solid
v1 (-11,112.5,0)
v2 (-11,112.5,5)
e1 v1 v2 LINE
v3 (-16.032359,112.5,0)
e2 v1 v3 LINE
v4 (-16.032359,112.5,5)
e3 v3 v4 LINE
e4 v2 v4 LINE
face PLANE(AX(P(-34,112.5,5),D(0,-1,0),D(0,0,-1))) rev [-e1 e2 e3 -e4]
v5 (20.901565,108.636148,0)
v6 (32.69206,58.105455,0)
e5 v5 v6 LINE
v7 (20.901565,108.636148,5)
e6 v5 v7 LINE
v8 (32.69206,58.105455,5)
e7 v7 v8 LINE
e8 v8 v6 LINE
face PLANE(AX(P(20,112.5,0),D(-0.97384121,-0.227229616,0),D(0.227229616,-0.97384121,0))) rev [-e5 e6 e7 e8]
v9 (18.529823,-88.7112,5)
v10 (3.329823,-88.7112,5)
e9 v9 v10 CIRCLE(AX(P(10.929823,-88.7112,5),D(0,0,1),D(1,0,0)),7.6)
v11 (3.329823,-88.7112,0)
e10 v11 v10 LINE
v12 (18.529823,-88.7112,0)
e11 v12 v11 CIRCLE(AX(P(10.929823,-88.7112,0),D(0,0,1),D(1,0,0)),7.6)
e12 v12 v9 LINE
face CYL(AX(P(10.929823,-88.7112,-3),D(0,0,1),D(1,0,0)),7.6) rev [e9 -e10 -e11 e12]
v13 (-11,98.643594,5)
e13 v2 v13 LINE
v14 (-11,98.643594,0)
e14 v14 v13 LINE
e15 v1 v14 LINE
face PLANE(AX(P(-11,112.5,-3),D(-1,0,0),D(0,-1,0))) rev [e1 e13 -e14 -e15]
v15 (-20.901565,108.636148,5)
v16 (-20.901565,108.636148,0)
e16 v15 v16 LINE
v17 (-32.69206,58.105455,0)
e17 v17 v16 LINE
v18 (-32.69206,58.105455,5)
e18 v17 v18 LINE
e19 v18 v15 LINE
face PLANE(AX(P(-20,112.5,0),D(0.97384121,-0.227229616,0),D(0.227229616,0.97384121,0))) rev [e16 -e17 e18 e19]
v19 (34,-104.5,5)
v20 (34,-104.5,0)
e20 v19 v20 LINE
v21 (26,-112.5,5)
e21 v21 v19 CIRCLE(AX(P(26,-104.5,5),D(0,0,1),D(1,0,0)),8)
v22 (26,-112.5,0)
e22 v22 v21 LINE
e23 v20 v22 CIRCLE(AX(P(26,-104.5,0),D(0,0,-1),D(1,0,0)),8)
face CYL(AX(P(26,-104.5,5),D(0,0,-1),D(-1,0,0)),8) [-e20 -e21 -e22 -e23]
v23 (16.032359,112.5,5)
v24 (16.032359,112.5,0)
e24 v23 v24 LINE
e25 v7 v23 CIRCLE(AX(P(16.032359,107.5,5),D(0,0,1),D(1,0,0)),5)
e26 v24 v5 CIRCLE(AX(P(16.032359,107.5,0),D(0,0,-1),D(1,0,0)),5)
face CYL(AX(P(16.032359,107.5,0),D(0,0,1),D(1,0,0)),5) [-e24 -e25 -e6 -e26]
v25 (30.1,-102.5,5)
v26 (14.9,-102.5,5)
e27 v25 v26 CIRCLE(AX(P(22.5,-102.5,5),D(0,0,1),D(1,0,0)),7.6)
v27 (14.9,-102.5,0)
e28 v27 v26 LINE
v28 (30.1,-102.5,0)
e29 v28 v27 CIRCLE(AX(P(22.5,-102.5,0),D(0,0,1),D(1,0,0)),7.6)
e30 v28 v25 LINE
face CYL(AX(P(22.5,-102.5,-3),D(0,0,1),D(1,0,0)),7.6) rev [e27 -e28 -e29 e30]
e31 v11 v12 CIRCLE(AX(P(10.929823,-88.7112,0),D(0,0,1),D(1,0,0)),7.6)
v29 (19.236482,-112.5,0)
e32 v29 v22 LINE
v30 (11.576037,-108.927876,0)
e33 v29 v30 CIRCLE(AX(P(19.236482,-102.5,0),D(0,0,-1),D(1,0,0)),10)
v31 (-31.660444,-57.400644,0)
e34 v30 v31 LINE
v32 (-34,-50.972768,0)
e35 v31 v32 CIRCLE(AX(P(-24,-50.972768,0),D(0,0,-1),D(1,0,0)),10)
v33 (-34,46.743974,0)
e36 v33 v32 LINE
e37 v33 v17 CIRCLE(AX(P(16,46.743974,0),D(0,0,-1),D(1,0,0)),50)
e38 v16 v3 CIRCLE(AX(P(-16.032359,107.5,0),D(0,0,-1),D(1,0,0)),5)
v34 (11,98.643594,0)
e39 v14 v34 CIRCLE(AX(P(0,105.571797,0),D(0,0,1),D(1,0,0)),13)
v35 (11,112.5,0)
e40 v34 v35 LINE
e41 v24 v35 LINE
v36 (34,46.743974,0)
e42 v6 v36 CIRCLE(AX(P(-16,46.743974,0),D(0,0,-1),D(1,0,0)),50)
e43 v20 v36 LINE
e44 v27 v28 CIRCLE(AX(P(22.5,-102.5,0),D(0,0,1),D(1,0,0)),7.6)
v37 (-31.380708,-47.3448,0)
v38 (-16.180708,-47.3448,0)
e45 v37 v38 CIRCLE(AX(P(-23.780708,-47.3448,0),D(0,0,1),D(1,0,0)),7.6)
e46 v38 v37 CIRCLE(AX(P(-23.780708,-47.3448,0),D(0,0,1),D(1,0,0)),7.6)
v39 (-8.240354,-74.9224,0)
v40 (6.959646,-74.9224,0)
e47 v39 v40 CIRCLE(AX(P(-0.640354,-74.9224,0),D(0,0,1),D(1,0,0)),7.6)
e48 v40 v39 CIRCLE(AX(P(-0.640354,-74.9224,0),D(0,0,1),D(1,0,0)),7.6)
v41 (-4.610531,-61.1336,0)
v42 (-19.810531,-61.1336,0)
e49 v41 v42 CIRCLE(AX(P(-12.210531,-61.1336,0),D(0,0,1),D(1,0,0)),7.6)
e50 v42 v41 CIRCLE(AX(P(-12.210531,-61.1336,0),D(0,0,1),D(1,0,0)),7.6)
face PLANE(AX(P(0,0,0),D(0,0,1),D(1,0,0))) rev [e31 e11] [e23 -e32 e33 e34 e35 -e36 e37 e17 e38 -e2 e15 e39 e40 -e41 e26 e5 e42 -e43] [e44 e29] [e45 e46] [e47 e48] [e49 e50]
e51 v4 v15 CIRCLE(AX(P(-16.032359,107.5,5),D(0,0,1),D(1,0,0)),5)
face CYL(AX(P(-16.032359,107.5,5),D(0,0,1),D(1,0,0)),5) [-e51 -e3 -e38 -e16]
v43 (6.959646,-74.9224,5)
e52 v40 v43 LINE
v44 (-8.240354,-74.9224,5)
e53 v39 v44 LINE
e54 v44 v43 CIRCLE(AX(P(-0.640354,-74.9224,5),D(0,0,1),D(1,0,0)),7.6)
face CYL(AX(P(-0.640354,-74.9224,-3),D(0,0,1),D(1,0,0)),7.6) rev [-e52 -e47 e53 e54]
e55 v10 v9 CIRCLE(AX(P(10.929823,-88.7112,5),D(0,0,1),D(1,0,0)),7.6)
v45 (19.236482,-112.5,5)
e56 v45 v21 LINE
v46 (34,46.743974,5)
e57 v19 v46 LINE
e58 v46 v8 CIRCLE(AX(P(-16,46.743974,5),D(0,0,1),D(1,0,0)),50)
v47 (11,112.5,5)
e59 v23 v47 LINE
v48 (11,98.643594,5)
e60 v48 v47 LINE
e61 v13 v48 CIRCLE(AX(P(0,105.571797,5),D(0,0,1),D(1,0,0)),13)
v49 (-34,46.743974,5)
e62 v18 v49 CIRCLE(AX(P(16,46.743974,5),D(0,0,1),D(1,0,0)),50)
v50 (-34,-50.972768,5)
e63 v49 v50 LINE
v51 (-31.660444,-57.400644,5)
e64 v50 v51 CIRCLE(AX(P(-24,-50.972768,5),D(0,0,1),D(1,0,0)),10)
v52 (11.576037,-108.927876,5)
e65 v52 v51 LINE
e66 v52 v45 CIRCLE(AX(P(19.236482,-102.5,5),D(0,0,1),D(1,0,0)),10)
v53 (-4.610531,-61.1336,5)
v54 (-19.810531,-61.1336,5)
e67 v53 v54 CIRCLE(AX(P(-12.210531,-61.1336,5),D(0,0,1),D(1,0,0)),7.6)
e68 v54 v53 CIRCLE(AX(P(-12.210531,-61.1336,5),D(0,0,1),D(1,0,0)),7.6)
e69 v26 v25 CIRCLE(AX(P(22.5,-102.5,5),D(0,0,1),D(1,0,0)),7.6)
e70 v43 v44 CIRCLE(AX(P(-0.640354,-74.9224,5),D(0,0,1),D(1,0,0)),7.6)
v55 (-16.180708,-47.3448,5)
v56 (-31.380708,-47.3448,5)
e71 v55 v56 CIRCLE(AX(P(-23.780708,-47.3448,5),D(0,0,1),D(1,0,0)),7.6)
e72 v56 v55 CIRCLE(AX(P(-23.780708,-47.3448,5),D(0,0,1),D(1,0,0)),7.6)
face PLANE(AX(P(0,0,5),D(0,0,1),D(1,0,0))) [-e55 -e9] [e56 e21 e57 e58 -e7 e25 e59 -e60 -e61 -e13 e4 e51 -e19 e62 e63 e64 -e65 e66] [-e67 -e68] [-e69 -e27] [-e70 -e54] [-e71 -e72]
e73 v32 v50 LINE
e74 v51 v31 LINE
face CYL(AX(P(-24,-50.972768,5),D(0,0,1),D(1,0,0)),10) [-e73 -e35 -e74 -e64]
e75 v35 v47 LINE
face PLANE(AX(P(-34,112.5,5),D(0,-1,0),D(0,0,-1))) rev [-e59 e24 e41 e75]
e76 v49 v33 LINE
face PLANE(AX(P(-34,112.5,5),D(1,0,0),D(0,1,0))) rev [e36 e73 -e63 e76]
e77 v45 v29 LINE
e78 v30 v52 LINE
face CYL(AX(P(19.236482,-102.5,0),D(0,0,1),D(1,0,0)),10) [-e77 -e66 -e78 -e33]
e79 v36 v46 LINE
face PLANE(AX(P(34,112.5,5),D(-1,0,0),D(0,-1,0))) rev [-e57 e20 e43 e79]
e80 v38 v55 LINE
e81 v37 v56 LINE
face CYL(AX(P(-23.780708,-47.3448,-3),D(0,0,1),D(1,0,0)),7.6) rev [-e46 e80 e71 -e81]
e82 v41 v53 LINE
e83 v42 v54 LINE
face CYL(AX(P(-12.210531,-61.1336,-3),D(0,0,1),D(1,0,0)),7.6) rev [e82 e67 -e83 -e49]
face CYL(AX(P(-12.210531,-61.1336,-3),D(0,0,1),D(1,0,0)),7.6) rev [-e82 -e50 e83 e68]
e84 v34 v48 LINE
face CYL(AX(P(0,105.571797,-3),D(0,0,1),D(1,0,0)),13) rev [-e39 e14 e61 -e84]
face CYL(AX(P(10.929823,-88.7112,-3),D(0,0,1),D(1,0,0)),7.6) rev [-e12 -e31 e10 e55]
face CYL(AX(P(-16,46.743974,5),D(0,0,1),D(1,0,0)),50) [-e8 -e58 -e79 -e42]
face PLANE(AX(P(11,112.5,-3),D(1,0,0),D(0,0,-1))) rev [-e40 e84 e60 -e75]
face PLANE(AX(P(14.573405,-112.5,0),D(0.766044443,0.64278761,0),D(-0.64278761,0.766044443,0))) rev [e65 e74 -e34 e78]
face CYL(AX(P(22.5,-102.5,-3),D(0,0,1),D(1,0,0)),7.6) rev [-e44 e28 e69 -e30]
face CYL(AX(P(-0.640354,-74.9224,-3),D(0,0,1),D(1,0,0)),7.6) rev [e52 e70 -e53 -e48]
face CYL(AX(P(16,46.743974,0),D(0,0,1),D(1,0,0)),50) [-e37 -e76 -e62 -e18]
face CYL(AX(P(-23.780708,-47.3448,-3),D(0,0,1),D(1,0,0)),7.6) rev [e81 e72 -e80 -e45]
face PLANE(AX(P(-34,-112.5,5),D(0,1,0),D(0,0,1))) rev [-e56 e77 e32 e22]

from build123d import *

# Parameters (mm, degrees)
SKETCH1_W           = 68
SKETCH1_H           = 225
BOSS_EXTRUDE1_DEPTH = 5
SKETCH3_R           = 7.6
CUT_EXTRUDE1_DEPTH  = 8
FILLET1_R           = 8
CUT_EXTRUDE2_DEPTH  = 118.631840928
FILLET2_R           = 10
CUT_EXTRUDE3_DEPTH  = 8
FILLET3_R           = 10
CUT_EXTRUDE4_DEPTH  = 118.631840928
FILLET4_R           = 5
FILLET5_R           = 50


with BuildPart() as part:
    # Sketch1 → Boss-Extrude1 (new body)
    with BuildSketch(Plane.XY):
        Rectangle(SKETCH1_W, SKETCH1_H)
    extrude(amount=BOSS_EXTRUDE1_DEPTH)

    # Sketch3 → Cut-Extrude1 (cut)
    with BuildSketch(Plane.XY.offset(5)):
        with Locations((22.5, -102.5)):
            Circle(SKETCH3_R)
        with Locations((10.929823026, -88.711200024)):
            Circle(SKETCH3_R)
        with Locations((-0.640353949, -74.922400048)):
            Circle(SKETCH3_R)
        with Locations((-12.210530923, -61.133600072)):
            Circle(SKETCH3_R)
        with Locations((-23.780707897, -47.344800095)):
            Circle(SKETCH3_R)
    extrude(amount=-CUT_EXTRUDE1_DEPTH, mode=Mode.SUBTRACT)

    # Fillet1
    fillet1_edges = [part.edges().sort_by_distance(p)[0] for p in [
        (34, -112.5, 2.5),
    ]]
    fillet(fillet1_edges, radius=FILLET1_R)

    # Sketch5 → Cut-Extrude2 (cut, through all)
    with BuildSketch(Plane.XY.offset(5)):
        Polygon((14.573405195, -112.5), (-34, -54.612469854), (-34, -112.5), align=None)
    extrude(amount=-CUT_EXTRUDE2_DEPTH, mode=Mode.SUBTRACT)

    # Fillet2
    fillet2_edges = [part.edges().sort_by_distance(p)[0] for p in [
        (14.573405195, -112.5, 2.5),
    ]]
    fillet(fillet2_edges, radius=FILLET2_R)

    # Sketch6 → Cut-Extrude3 (cut)
    with BuildSketch(Plane.XY.offset(5)):
        with BuildLine():
            Line((-11, 112.5), (-11, 98.643593539))
            ThreePointArc((-11, 98.643593539), (0, 92.57179677), (11, 98.643593539))
            Line((11, 98.643593539), (11, 112.5))
            ThreePointArc((11, 112.5), (0, 118.57179677), (-11, 112.5))
        make_face()
    extrude(amount=-CUT_EXTRUDE3_DEPTH, mode=Mode.SUBTRACT)

    # Fillet3
    fillet3_edges = [part.edges().sort_by_distance(p)[0] for p in [
        (-34, -54.612469854, 2.5),
    ]]
    fillet(fillet3_edges, radius=FILLET3_R)

    # Sketch7 → Cut-Extrude4 (cut, through all)
    with BuildSketch(Plane.XY.offset(5)):
        Polygon((-20, 112.5), (-34, 52.5), (-34, 112.5), align=None)
        Polygon((34, 112.5), (20, 112.5), (34, 52.5), align=None)
    extrude(amount=-CUT_EXTRUDE4_DEPTH, mode=Mode.SUBTRACT)

    # Fillet4
    fillet4_edges = [part.edges().sort_by_distance(p)[0] for p in [
        (20, 112.5, 2.5),
        (-20, 112.5, 2.5),
    ]]
    fillet(fillet4_edges, radius=FILLET4_R)

    # Fillet5
    fillet5_edges = [part.edges().sort_by_distance(p)[0] for p in [
        (34, 52.5, 2.5),
        (-34, 52.5, 2.5),
    ]]
    fillet(fillet5_edges, radius=FILLET5_R)


solid = part.part
